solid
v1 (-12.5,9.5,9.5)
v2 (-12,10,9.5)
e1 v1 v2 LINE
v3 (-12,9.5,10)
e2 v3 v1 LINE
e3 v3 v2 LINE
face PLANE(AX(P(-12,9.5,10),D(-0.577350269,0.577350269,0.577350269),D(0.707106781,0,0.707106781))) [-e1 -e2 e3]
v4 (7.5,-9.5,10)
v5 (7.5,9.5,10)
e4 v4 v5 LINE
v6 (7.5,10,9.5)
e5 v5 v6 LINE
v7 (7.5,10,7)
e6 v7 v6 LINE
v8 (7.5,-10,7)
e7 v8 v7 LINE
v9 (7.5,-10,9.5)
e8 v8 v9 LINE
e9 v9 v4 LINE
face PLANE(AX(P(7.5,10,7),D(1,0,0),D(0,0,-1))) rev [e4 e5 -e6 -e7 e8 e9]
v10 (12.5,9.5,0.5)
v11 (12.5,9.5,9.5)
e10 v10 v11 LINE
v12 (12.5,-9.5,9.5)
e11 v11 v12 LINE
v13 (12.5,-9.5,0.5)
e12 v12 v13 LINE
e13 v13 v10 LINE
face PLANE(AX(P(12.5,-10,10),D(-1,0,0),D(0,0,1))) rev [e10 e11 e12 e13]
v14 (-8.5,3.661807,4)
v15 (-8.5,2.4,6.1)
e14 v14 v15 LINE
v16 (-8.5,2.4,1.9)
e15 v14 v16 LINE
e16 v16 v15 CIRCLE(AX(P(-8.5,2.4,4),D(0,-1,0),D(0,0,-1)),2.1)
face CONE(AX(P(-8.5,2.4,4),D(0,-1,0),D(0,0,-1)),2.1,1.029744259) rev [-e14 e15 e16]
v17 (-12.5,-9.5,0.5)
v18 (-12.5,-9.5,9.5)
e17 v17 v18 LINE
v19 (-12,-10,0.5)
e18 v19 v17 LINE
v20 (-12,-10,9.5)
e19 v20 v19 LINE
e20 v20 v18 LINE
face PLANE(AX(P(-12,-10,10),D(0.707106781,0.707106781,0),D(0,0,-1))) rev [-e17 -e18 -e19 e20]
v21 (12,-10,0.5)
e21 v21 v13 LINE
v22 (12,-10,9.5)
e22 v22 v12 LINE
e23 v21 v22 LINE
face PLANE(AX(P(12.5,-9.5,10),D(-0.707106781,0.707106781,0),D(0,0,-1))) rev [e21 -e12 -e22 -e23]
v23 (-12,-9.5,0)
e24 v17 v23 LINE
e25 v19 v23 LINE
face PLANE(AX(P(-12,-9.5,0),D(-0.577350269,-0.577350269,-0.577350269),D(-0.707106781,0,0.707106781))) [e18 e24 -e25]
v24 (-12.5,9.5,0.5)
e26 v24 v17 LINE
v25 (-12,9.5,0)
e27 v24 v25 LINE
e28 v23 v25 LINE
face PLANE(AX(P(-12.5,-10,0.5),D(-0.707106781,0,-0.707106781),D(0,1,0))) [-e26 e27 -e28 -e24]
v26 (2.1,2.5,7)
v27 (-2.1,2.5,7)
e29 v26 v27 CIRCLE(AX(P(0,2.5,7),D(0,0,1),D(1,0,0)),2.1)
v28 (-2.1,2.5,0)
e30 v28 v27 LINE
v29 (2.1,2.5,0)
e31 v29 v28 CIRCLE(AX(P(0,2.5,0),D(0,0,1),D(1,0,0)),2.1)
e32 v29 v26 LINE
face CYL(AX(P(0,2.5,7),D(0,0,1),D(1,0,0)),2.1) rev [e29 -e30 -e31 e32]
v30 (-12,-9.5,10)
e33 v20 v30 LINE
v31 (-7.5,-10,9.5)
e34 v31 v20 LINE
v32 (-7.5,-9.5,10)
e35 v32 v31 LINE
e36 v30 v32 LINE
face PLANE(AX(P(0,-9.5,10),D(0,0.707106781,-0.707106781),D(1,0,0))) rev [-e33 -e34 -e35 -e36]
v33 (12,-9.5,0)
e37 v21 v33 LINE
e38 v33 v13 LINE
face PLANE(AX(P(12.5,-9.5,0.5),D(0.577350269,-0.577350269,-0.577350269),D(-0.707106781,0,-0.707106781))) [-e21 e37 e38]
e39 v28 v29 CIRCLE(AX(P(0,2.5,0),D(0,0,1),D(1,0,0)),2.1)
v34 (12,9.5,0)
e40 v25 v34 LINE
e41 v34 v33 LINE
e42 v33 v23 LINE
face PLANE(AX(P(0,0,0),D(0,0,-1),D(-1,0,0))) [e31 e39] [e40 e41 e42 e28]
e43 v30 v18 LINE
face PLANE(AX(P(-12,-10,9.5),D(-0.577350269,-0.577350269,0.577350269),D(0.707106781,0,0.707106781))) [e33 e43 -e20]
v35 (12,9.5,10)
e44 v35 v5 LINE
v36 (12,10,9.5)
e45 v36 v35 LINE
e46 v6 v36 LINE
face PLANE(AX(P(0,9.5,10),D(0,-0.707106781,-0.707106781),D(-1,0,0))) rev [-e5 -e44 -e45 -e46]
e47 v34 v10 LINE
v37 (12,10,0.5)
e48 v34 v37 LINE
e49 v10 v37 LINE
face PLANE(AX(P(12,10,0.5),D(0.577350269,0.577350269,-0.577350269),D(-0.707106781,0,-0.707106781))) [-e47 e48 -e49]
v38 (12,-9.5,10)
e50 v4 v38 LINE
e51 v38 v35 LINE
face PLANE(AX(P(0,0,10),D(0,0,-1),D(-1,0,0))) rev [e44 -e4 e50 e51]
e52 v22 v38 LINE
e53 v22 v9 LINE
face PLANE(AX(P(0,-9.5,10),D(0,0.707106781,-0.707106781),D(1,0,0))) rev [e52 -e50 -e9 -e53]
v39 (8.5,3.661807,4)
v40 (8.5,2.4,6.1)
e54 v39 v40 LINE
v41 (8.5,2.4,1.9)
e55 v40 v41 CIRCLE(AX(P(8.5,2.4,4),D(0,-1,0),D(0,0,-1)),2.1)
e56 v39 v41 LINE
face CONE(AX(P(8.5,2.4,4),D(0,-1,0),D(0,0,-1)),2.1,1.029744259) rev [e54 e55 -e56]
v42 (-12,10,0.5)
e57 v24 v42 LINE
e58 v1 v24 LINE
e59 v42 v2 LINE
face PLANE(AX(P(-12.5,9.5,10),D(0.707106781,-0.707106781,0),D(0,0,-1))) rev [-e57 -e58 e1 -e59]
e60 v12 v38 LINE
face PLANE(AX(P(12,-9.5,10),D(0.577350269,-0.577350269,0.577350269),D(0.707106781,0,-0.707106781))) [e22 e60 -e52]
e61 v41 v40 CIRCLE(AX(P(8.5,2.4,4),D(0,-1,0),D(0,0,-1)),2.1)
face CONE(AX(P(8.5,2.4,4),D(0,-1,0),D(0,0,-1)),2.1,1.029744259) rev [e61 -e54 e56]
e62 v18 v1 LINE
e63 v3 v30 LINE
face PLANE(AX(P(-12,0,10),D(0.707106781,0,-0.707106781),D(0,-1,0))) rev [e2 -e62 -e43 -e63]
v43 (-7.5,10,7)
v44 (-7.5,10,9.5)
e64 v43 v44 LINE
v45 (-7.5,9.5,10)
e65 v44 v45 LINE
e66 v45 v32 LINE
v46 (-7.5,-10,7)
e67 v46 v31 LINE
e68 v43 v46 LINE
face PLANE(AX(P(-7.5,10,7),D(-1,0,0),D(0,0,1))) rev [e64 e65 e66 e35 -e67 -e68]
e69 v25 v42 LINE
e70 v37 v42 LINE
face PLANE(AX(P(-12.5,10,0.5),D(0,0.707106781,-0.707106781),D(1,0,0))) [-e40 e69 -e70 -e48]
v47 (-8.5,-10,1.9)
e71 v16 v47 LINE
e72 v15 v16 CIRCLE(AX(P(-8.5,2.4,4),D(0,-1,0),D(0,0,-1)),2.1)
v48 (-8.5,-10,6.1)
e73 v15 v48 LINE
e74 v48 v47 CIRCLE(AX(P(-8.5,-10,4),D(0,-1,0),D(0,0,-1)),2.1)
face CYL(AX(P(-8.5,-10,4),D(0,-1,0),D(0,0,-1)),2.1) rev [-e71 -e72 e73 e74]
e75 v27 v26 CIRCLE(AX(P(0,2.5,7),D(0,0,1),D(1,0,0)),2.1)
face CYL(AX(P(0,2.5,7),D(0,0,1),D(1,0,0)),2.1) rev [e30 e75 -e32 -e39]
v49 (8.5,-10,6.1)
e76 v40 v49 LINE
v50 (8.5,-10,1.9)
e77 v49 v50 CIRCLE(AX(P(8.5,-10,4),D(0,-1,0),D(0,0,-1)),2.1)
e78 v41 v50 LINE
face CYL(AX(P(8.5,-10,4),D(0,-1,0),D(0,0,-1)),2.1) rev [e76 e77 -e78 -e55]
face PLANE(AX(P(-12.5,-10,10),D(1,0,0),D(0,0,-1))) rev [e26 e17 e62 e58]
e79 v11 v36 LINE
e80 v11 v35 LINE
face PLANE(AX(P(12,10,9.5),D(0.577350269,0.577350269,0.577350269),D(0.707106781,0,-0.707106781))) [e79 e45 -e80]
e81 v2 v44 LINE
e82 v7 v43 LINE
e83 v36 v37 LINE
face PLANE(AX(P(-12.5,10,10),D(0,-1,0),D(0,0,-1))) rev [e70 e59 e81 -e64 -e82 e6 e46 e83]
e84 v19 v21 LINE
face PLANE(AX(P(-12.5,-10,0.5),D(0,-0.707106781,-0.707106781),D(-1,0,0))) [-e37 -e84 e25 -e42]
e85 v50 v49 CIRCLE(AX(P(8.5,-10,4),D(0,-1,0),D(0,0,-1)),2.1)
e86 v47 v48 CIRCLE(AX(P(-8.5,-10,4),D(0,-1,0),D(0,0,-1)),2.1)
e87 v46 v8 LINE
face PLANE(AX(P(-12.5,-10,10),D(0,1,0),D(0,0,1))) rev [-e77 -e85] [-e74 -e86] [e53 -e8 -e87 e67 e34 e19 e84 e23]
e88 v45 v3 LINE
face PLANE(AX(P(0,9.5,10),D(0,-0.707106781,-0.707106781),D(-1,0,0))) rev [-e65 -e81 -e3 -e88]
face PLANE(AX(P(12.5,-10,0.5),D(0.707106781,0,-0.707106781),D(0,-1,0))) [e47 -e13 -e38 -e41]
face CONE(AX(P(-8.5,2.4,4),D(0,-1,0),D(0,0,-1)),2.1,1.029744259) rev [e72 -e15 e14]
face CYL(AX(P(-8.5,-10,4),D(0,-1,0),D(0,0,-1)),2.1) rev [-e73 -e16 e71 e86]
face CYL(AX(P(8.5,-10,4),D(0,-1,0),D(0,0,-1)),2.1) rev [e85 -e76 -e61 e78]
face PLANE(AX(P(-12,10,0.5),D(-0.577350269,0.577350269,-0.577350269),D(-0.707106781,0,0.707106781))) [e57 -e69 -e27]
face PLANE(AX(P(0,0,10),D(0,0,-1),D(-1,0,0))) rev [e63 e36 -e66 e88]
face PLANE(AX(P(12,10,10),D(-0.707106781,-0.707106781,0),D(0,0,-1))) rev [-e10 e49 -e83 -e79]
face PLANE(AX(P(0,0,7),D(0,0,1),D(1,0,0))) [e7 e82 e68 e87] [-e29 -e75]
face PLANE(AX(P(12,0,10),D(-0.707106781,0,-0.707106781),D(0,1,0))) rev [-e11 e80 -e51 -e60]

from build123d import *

# Parameters (mm, degrees)
SKETCH1_W             = 25
SKETCH1_H             = 20
BOSS_EXTRUDE1_DEPTH   = 10
SKETCH2_W             = 15
SKETCH2_H             = 20
CUT_EXTRUDE1_DEPTH    = 3
M5_TAPPED_HOLE1_D     = 4.2
M5_TAPPED_HOLE2_D     = 4.2
M5_TAPPED_HOLE2_DEPTH = 12.4
M5_TAPPED_HOLE2_TIP   = 1.2618073
CHAMFER1_SIZE         = 0.5


with BuildPart() as part:
    # Sketch1 → Boss-Extrude1 (new body)
    with BuildSketch(Plane.XY):
        Rectangle(SKETCH1_W, SKETCH1_H)
    extrude(amount=BOSS_EXTRUDE1_DEPTH)

    # Sketch2 → Cut-Extrude1 (cut)
    with BuildSketch(Plane.XY.offset(10)):
        Rectangle(SKETCH2_W, SKETCH2_H)
    extrude(amount=-CUT_EXTRUDE1_DEPTH, mode=Mode.SUBTRACT)

    # M5 Tapped Hole1 (through all)
    with Locations(Plane.XY.offset(7)):
        with Locations((0, 2.5)):
            Hole(M5_TAPPED_HOLE1_D / 2)

    # M5 Tapped Hole2
    with Locations(Plane(origin=(0, -10, 0), x_dir=(-1, 0, 0), z_dir=(0, -1, 0))):
        with Locations((8.5, -4), (-8.5, -4)):
            Hole(M5_TAPPED_HOLE2_D / 2, depth=M5_TAPPED_HOLE2_DEPTH)
            with Locations((0, 0, -(M5_TAPPED_HOLE2_DEPTH + M5_TAPPED_HOLE2_TIP / 2))):  # 118° drill point
                Cone(0, M5_TAPPED_HOLE2_D / 2, M5_TAPPED_HOLE2_TIP, mode=Mode.SUBTRACT)

    # Chamfer1
    chamfer1_edges = [part.edges().sort_by_distance(p)[0] for p in [
        (-12.5, 0, 10),
        (-10, -10, 10),
        (-10, 10, 10),
        (10, -10, 10),
        (12.5, 0, 10),
        (0, -10, 0),
        (-12.5, 0, 0),
        (0, 10, 0),
        (12.5, 0, 0),
        (10, 10, 10),
        (12.5, -10, 5),
        (-12.5, -10, 5),
        (-12.5, 10, 5),
        (12.5, 10, 5),
    ]]
    chamfer(chamfer1_edges, length=CHAMFER1_SIZE)


solid = part.part
